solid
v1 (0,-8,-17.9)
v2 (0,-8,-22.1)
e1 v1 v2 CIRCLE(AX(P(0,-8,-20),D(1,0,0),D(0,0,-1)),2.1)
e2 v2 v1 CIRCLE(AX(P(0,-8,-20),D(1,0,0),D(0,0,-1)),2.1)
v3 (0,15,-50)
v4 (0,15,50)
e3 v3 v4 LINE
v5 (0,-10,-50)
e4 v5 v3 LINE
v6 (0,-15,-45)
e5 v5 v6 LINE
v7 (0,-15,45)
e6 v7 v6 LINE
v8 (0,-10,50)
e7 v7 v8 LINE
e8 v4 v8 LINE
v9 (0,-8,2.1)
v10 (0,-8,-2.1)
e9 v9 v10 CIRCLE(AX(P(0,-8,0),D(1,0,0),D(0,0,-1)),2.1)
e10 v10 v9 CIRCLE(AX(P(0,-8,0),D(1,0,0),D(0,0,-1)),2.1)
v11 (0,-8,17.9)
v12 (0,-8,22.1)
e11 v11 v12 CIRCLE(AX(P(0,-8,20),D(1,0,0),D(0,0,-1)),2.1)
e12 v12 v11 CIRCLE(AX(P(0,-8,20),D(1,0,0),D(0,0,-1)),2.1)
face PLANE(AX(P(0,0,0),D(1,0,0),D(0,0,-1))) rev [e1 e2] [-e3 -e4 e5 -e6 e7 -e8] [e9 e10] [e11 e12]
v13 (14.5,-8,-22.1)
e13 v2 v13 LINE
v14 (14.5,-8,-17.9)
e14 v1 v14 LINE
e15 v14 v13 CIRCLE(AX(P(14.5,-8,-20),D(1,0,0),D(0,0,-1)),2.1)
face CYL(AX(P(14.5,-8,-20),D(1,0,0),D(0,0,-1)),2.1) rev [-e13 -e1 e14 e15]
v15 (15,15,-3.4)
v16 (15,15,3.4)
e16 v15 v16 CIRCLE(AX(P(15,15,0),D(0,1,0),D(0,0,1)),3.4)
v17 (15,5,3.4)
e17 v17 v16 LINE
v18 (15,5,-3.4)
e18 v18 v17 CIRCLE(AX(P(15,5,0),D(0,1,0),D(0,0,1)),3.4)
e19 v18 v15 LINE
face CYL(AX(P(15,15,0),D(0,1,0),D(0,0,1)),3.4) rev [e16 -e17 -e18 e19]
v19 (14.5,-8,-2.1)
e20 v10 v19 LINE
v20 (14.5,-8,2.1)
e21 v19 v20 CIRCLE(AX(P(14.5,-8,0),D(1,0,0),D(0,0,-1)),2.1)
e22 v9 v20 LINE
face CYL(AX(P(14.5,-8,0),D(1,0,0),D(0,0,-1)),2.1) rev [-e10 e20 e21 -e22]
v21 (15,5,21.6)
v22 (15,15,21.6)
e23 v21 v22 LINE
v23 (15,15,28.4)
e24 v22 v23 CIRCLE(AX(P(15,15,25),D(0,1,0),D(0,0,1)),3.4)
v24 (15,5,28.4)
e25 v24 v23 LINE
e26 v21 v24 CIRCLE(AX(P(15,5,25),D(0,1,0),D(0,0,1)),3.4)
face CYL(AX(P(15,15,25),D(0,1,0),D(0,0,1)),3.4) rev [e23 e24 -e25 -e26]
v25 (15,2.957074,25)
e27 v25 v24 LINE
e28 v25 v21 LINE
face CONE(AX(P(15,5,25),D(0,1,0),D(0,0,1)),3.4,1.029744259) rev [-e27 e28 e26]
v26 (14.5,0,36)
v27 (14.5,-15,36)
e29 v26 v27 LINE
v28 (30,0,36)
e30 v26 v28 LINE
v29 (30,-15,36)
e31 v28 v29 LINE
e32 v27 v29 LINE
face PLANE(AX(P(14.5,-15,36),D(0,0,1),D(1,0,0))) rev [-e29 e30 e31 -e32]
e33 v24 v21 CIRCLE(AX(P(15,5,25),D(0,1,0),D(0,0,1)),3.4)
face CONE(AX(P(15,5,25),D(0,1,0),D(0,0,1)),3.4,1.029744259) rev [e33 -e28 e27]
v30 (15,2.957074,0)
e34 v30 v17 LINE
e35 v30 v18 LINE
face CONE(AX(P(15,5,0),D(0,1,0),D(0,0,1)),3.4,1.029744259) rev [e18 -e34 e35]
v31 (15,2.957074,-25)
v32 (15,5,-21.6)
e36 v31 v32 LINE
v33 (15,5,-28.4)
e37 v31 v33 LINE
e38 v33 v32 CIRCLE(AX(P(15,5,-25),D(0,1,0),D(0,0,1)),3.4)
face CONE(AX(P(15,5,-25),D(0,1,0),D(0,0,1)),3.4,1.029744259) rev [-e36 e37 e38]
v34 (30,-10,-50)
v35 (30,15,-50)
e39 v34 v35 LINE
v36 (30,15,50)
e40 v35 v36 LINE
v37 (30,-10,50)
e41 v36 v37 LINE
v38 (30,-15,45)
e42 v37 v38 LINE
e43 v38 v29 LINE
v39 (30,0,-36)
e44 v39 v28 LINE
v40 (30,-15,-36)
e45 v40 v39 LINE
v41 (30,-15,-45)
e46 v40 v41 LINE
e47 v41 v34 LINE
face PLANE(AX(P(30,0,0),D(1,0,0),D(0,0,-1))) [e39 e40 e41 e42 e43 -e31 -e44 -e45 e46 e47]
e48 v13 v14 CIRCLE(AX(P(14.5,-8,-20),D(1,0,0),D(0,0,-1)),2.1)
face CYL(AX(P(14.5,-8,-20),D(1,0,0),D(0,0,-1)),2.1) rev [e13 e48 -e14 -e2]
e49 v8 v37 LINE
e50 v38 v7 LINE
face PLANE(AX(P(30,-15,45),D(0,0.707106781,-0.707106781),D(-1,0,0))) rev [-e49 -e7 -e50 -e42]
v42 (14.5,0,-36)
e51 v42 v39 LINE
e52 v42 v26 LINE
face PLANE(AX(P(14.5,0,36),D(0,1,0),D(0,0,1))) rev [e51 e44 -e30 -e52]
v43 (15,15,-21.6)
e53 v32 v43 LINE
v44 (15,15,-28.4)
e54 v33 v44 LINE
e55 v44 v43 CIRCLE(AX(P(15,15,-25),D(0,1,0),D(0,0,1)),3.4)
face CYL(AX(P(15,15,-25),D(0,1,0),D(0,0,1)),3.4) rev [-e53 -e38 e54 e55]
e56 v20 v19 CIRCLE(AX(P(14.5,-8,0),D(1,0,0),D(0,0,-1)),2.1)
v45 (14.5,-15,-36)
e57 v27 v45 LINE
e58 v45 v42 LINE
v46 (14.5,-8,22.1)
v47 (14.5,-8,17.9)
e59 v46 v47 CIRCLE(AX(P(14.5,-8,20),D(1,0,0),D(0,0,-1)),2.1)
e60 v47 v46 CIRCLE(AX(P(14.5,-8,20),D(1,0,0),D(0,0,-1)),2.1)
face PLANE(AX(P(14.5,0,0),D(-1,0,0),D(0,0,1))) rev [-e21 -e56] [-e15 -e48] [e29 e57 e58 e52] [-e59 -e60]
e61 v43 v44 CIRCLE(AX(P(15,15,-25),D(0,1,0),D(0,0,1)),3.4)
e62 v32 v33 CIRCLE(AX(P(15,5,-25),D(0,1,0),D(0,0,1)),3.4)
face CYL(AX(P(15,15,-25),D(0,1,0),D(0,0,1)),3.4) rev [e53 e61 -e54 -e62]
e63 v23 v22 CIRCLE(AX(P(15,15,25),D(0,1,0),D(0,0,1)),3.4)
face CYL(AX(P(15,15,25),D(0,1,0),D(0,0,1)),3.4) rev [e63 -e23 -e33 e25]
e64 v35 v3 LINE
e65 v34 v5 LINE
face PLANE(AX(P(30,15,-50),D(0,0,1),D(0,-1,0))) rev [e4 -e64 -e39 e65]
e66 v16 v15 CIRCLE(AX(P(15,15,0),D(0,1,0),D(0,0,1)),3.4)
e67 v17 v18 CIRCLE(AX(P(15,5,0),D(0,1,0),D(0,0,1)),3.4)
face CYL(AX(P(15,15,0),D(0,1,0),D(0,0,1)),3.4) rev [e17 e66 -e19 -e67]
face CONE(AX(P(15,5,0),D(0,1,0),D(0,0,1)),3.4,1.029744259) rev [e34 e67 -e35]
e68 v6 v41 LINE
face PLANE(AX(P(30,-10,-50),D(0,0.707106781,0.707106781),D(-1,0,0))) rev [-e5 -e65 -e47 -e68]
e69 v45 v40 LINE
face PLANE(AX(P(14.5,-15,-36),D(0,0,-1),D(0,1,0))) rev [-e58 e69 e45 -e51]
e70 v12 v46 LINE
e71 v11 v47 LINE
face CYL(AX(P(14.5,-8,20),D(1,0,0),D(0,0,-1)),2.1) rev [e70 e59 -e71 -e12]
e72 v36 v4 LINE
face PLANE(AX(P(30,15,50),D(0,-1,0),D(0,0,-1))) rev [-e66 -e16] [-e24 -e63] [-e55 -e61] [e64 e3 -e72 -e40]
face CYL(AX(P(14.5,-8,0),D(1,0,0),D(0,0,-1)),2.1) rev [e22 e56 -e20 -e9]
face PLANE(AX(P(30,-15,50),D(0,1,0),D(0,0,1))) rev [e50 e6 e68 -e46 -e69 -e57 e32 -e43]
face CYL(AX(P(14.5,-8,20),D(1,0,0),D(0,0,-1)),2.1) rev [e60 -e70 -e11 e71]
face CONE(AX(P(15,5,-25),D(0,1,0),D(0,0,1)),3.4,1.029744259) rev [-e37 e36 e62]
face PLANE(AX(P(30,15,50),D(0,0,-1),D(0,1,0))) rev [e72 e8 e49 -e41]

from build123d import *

# Parameters (mm, degrees)
SKETCH_1_W             = 100
SKETCH_1_H             = 30
EXTRUDE_1_DEPTH        = 30
SKETCH_2_W             = 72
SKETCH_2_H             = 15
CUT_EXTRUDE_1_DEPTH    = 15.5
HOLE_WIZARD_M8_1_D     = 6.8
HOLE_WIZARD_M8_1_DEPTH = 10
HOLE_WIZARD_M8_1_TIP   = 2.042926105
HOLE_WIZARD_M5_1_D     = 4.2
CHAMFER_1_SIZE         = 5


with BuildPart() as part:
    # 草图1 → 凸台-拉伸1 (new body)
    with BuildSketch(Plane(origin=(0, 0, 0), x_dir=(0, 0, -1), z_dir=(1, 0, 0))):
        Rectangle(SKETCH_1_W, SKETCH_1_H)
    extrude(amount=EXTRUDE_1_DEPTH)

    # 草图2 → 切除-拉伸1 (cut)
    with BuildSketch(Plane(origin=(30, 0, 0), x_dir=(0, 0, -1), z_dir=(1, 0, 0))):
        with Locations((0, -7.5)):
            Rectangle(SKETCH_2_W, SKETCH_2_H)
    extrude(amount=-CUT_EXTRUDE_1_DEPTH, mode=Mode.SUBTRACT)

    # M8 螺纹孔1
    with Locations(Plane(origin=(0, 15, 0), x_dir=(1, 0, 0), z_dir=(0, 1, 0))):
        with Locations((15, 0), (15, 25), (15, -25)):
            Hole(HOLE_WIZARD_M8_1_D / 2, depth=HOLE_WIZARD_M8_1_DEPTH)
            with Locations((0, 0, -(HOLE_WIZARD_M8_1_DEPTH + HOLE_WIZARD_M8_1_TIP / 2))):  # 118° drill point
                Cone(0, HOLE_WIZARD_M8_1_D / 2, HOLE_WIZARD_M8_1_TIP, mode=Mode.SUBTRACT)

    # M5 螺纹孔1 (through all)
    with Locations(Plane(origin=(14.5, 0, 0), x_dir=(0, 0, -1), z_dir=(1, 0, 0))):
        with Locations((-20, -8), (0, -8), (20, -8)):
            Hole(HOLE_WIZARD_M5_1_D / 2)

    # 倒角1
    chamfer_1_edges = [part.edges().sort_by_distance(p)[0] for p in [
        (15, -15, -50),
        (15, -15, 50),
    ]]
    chamfer(chamfer_1_edges, length=CHAMFER_1_SIZE)


solid = part.part
